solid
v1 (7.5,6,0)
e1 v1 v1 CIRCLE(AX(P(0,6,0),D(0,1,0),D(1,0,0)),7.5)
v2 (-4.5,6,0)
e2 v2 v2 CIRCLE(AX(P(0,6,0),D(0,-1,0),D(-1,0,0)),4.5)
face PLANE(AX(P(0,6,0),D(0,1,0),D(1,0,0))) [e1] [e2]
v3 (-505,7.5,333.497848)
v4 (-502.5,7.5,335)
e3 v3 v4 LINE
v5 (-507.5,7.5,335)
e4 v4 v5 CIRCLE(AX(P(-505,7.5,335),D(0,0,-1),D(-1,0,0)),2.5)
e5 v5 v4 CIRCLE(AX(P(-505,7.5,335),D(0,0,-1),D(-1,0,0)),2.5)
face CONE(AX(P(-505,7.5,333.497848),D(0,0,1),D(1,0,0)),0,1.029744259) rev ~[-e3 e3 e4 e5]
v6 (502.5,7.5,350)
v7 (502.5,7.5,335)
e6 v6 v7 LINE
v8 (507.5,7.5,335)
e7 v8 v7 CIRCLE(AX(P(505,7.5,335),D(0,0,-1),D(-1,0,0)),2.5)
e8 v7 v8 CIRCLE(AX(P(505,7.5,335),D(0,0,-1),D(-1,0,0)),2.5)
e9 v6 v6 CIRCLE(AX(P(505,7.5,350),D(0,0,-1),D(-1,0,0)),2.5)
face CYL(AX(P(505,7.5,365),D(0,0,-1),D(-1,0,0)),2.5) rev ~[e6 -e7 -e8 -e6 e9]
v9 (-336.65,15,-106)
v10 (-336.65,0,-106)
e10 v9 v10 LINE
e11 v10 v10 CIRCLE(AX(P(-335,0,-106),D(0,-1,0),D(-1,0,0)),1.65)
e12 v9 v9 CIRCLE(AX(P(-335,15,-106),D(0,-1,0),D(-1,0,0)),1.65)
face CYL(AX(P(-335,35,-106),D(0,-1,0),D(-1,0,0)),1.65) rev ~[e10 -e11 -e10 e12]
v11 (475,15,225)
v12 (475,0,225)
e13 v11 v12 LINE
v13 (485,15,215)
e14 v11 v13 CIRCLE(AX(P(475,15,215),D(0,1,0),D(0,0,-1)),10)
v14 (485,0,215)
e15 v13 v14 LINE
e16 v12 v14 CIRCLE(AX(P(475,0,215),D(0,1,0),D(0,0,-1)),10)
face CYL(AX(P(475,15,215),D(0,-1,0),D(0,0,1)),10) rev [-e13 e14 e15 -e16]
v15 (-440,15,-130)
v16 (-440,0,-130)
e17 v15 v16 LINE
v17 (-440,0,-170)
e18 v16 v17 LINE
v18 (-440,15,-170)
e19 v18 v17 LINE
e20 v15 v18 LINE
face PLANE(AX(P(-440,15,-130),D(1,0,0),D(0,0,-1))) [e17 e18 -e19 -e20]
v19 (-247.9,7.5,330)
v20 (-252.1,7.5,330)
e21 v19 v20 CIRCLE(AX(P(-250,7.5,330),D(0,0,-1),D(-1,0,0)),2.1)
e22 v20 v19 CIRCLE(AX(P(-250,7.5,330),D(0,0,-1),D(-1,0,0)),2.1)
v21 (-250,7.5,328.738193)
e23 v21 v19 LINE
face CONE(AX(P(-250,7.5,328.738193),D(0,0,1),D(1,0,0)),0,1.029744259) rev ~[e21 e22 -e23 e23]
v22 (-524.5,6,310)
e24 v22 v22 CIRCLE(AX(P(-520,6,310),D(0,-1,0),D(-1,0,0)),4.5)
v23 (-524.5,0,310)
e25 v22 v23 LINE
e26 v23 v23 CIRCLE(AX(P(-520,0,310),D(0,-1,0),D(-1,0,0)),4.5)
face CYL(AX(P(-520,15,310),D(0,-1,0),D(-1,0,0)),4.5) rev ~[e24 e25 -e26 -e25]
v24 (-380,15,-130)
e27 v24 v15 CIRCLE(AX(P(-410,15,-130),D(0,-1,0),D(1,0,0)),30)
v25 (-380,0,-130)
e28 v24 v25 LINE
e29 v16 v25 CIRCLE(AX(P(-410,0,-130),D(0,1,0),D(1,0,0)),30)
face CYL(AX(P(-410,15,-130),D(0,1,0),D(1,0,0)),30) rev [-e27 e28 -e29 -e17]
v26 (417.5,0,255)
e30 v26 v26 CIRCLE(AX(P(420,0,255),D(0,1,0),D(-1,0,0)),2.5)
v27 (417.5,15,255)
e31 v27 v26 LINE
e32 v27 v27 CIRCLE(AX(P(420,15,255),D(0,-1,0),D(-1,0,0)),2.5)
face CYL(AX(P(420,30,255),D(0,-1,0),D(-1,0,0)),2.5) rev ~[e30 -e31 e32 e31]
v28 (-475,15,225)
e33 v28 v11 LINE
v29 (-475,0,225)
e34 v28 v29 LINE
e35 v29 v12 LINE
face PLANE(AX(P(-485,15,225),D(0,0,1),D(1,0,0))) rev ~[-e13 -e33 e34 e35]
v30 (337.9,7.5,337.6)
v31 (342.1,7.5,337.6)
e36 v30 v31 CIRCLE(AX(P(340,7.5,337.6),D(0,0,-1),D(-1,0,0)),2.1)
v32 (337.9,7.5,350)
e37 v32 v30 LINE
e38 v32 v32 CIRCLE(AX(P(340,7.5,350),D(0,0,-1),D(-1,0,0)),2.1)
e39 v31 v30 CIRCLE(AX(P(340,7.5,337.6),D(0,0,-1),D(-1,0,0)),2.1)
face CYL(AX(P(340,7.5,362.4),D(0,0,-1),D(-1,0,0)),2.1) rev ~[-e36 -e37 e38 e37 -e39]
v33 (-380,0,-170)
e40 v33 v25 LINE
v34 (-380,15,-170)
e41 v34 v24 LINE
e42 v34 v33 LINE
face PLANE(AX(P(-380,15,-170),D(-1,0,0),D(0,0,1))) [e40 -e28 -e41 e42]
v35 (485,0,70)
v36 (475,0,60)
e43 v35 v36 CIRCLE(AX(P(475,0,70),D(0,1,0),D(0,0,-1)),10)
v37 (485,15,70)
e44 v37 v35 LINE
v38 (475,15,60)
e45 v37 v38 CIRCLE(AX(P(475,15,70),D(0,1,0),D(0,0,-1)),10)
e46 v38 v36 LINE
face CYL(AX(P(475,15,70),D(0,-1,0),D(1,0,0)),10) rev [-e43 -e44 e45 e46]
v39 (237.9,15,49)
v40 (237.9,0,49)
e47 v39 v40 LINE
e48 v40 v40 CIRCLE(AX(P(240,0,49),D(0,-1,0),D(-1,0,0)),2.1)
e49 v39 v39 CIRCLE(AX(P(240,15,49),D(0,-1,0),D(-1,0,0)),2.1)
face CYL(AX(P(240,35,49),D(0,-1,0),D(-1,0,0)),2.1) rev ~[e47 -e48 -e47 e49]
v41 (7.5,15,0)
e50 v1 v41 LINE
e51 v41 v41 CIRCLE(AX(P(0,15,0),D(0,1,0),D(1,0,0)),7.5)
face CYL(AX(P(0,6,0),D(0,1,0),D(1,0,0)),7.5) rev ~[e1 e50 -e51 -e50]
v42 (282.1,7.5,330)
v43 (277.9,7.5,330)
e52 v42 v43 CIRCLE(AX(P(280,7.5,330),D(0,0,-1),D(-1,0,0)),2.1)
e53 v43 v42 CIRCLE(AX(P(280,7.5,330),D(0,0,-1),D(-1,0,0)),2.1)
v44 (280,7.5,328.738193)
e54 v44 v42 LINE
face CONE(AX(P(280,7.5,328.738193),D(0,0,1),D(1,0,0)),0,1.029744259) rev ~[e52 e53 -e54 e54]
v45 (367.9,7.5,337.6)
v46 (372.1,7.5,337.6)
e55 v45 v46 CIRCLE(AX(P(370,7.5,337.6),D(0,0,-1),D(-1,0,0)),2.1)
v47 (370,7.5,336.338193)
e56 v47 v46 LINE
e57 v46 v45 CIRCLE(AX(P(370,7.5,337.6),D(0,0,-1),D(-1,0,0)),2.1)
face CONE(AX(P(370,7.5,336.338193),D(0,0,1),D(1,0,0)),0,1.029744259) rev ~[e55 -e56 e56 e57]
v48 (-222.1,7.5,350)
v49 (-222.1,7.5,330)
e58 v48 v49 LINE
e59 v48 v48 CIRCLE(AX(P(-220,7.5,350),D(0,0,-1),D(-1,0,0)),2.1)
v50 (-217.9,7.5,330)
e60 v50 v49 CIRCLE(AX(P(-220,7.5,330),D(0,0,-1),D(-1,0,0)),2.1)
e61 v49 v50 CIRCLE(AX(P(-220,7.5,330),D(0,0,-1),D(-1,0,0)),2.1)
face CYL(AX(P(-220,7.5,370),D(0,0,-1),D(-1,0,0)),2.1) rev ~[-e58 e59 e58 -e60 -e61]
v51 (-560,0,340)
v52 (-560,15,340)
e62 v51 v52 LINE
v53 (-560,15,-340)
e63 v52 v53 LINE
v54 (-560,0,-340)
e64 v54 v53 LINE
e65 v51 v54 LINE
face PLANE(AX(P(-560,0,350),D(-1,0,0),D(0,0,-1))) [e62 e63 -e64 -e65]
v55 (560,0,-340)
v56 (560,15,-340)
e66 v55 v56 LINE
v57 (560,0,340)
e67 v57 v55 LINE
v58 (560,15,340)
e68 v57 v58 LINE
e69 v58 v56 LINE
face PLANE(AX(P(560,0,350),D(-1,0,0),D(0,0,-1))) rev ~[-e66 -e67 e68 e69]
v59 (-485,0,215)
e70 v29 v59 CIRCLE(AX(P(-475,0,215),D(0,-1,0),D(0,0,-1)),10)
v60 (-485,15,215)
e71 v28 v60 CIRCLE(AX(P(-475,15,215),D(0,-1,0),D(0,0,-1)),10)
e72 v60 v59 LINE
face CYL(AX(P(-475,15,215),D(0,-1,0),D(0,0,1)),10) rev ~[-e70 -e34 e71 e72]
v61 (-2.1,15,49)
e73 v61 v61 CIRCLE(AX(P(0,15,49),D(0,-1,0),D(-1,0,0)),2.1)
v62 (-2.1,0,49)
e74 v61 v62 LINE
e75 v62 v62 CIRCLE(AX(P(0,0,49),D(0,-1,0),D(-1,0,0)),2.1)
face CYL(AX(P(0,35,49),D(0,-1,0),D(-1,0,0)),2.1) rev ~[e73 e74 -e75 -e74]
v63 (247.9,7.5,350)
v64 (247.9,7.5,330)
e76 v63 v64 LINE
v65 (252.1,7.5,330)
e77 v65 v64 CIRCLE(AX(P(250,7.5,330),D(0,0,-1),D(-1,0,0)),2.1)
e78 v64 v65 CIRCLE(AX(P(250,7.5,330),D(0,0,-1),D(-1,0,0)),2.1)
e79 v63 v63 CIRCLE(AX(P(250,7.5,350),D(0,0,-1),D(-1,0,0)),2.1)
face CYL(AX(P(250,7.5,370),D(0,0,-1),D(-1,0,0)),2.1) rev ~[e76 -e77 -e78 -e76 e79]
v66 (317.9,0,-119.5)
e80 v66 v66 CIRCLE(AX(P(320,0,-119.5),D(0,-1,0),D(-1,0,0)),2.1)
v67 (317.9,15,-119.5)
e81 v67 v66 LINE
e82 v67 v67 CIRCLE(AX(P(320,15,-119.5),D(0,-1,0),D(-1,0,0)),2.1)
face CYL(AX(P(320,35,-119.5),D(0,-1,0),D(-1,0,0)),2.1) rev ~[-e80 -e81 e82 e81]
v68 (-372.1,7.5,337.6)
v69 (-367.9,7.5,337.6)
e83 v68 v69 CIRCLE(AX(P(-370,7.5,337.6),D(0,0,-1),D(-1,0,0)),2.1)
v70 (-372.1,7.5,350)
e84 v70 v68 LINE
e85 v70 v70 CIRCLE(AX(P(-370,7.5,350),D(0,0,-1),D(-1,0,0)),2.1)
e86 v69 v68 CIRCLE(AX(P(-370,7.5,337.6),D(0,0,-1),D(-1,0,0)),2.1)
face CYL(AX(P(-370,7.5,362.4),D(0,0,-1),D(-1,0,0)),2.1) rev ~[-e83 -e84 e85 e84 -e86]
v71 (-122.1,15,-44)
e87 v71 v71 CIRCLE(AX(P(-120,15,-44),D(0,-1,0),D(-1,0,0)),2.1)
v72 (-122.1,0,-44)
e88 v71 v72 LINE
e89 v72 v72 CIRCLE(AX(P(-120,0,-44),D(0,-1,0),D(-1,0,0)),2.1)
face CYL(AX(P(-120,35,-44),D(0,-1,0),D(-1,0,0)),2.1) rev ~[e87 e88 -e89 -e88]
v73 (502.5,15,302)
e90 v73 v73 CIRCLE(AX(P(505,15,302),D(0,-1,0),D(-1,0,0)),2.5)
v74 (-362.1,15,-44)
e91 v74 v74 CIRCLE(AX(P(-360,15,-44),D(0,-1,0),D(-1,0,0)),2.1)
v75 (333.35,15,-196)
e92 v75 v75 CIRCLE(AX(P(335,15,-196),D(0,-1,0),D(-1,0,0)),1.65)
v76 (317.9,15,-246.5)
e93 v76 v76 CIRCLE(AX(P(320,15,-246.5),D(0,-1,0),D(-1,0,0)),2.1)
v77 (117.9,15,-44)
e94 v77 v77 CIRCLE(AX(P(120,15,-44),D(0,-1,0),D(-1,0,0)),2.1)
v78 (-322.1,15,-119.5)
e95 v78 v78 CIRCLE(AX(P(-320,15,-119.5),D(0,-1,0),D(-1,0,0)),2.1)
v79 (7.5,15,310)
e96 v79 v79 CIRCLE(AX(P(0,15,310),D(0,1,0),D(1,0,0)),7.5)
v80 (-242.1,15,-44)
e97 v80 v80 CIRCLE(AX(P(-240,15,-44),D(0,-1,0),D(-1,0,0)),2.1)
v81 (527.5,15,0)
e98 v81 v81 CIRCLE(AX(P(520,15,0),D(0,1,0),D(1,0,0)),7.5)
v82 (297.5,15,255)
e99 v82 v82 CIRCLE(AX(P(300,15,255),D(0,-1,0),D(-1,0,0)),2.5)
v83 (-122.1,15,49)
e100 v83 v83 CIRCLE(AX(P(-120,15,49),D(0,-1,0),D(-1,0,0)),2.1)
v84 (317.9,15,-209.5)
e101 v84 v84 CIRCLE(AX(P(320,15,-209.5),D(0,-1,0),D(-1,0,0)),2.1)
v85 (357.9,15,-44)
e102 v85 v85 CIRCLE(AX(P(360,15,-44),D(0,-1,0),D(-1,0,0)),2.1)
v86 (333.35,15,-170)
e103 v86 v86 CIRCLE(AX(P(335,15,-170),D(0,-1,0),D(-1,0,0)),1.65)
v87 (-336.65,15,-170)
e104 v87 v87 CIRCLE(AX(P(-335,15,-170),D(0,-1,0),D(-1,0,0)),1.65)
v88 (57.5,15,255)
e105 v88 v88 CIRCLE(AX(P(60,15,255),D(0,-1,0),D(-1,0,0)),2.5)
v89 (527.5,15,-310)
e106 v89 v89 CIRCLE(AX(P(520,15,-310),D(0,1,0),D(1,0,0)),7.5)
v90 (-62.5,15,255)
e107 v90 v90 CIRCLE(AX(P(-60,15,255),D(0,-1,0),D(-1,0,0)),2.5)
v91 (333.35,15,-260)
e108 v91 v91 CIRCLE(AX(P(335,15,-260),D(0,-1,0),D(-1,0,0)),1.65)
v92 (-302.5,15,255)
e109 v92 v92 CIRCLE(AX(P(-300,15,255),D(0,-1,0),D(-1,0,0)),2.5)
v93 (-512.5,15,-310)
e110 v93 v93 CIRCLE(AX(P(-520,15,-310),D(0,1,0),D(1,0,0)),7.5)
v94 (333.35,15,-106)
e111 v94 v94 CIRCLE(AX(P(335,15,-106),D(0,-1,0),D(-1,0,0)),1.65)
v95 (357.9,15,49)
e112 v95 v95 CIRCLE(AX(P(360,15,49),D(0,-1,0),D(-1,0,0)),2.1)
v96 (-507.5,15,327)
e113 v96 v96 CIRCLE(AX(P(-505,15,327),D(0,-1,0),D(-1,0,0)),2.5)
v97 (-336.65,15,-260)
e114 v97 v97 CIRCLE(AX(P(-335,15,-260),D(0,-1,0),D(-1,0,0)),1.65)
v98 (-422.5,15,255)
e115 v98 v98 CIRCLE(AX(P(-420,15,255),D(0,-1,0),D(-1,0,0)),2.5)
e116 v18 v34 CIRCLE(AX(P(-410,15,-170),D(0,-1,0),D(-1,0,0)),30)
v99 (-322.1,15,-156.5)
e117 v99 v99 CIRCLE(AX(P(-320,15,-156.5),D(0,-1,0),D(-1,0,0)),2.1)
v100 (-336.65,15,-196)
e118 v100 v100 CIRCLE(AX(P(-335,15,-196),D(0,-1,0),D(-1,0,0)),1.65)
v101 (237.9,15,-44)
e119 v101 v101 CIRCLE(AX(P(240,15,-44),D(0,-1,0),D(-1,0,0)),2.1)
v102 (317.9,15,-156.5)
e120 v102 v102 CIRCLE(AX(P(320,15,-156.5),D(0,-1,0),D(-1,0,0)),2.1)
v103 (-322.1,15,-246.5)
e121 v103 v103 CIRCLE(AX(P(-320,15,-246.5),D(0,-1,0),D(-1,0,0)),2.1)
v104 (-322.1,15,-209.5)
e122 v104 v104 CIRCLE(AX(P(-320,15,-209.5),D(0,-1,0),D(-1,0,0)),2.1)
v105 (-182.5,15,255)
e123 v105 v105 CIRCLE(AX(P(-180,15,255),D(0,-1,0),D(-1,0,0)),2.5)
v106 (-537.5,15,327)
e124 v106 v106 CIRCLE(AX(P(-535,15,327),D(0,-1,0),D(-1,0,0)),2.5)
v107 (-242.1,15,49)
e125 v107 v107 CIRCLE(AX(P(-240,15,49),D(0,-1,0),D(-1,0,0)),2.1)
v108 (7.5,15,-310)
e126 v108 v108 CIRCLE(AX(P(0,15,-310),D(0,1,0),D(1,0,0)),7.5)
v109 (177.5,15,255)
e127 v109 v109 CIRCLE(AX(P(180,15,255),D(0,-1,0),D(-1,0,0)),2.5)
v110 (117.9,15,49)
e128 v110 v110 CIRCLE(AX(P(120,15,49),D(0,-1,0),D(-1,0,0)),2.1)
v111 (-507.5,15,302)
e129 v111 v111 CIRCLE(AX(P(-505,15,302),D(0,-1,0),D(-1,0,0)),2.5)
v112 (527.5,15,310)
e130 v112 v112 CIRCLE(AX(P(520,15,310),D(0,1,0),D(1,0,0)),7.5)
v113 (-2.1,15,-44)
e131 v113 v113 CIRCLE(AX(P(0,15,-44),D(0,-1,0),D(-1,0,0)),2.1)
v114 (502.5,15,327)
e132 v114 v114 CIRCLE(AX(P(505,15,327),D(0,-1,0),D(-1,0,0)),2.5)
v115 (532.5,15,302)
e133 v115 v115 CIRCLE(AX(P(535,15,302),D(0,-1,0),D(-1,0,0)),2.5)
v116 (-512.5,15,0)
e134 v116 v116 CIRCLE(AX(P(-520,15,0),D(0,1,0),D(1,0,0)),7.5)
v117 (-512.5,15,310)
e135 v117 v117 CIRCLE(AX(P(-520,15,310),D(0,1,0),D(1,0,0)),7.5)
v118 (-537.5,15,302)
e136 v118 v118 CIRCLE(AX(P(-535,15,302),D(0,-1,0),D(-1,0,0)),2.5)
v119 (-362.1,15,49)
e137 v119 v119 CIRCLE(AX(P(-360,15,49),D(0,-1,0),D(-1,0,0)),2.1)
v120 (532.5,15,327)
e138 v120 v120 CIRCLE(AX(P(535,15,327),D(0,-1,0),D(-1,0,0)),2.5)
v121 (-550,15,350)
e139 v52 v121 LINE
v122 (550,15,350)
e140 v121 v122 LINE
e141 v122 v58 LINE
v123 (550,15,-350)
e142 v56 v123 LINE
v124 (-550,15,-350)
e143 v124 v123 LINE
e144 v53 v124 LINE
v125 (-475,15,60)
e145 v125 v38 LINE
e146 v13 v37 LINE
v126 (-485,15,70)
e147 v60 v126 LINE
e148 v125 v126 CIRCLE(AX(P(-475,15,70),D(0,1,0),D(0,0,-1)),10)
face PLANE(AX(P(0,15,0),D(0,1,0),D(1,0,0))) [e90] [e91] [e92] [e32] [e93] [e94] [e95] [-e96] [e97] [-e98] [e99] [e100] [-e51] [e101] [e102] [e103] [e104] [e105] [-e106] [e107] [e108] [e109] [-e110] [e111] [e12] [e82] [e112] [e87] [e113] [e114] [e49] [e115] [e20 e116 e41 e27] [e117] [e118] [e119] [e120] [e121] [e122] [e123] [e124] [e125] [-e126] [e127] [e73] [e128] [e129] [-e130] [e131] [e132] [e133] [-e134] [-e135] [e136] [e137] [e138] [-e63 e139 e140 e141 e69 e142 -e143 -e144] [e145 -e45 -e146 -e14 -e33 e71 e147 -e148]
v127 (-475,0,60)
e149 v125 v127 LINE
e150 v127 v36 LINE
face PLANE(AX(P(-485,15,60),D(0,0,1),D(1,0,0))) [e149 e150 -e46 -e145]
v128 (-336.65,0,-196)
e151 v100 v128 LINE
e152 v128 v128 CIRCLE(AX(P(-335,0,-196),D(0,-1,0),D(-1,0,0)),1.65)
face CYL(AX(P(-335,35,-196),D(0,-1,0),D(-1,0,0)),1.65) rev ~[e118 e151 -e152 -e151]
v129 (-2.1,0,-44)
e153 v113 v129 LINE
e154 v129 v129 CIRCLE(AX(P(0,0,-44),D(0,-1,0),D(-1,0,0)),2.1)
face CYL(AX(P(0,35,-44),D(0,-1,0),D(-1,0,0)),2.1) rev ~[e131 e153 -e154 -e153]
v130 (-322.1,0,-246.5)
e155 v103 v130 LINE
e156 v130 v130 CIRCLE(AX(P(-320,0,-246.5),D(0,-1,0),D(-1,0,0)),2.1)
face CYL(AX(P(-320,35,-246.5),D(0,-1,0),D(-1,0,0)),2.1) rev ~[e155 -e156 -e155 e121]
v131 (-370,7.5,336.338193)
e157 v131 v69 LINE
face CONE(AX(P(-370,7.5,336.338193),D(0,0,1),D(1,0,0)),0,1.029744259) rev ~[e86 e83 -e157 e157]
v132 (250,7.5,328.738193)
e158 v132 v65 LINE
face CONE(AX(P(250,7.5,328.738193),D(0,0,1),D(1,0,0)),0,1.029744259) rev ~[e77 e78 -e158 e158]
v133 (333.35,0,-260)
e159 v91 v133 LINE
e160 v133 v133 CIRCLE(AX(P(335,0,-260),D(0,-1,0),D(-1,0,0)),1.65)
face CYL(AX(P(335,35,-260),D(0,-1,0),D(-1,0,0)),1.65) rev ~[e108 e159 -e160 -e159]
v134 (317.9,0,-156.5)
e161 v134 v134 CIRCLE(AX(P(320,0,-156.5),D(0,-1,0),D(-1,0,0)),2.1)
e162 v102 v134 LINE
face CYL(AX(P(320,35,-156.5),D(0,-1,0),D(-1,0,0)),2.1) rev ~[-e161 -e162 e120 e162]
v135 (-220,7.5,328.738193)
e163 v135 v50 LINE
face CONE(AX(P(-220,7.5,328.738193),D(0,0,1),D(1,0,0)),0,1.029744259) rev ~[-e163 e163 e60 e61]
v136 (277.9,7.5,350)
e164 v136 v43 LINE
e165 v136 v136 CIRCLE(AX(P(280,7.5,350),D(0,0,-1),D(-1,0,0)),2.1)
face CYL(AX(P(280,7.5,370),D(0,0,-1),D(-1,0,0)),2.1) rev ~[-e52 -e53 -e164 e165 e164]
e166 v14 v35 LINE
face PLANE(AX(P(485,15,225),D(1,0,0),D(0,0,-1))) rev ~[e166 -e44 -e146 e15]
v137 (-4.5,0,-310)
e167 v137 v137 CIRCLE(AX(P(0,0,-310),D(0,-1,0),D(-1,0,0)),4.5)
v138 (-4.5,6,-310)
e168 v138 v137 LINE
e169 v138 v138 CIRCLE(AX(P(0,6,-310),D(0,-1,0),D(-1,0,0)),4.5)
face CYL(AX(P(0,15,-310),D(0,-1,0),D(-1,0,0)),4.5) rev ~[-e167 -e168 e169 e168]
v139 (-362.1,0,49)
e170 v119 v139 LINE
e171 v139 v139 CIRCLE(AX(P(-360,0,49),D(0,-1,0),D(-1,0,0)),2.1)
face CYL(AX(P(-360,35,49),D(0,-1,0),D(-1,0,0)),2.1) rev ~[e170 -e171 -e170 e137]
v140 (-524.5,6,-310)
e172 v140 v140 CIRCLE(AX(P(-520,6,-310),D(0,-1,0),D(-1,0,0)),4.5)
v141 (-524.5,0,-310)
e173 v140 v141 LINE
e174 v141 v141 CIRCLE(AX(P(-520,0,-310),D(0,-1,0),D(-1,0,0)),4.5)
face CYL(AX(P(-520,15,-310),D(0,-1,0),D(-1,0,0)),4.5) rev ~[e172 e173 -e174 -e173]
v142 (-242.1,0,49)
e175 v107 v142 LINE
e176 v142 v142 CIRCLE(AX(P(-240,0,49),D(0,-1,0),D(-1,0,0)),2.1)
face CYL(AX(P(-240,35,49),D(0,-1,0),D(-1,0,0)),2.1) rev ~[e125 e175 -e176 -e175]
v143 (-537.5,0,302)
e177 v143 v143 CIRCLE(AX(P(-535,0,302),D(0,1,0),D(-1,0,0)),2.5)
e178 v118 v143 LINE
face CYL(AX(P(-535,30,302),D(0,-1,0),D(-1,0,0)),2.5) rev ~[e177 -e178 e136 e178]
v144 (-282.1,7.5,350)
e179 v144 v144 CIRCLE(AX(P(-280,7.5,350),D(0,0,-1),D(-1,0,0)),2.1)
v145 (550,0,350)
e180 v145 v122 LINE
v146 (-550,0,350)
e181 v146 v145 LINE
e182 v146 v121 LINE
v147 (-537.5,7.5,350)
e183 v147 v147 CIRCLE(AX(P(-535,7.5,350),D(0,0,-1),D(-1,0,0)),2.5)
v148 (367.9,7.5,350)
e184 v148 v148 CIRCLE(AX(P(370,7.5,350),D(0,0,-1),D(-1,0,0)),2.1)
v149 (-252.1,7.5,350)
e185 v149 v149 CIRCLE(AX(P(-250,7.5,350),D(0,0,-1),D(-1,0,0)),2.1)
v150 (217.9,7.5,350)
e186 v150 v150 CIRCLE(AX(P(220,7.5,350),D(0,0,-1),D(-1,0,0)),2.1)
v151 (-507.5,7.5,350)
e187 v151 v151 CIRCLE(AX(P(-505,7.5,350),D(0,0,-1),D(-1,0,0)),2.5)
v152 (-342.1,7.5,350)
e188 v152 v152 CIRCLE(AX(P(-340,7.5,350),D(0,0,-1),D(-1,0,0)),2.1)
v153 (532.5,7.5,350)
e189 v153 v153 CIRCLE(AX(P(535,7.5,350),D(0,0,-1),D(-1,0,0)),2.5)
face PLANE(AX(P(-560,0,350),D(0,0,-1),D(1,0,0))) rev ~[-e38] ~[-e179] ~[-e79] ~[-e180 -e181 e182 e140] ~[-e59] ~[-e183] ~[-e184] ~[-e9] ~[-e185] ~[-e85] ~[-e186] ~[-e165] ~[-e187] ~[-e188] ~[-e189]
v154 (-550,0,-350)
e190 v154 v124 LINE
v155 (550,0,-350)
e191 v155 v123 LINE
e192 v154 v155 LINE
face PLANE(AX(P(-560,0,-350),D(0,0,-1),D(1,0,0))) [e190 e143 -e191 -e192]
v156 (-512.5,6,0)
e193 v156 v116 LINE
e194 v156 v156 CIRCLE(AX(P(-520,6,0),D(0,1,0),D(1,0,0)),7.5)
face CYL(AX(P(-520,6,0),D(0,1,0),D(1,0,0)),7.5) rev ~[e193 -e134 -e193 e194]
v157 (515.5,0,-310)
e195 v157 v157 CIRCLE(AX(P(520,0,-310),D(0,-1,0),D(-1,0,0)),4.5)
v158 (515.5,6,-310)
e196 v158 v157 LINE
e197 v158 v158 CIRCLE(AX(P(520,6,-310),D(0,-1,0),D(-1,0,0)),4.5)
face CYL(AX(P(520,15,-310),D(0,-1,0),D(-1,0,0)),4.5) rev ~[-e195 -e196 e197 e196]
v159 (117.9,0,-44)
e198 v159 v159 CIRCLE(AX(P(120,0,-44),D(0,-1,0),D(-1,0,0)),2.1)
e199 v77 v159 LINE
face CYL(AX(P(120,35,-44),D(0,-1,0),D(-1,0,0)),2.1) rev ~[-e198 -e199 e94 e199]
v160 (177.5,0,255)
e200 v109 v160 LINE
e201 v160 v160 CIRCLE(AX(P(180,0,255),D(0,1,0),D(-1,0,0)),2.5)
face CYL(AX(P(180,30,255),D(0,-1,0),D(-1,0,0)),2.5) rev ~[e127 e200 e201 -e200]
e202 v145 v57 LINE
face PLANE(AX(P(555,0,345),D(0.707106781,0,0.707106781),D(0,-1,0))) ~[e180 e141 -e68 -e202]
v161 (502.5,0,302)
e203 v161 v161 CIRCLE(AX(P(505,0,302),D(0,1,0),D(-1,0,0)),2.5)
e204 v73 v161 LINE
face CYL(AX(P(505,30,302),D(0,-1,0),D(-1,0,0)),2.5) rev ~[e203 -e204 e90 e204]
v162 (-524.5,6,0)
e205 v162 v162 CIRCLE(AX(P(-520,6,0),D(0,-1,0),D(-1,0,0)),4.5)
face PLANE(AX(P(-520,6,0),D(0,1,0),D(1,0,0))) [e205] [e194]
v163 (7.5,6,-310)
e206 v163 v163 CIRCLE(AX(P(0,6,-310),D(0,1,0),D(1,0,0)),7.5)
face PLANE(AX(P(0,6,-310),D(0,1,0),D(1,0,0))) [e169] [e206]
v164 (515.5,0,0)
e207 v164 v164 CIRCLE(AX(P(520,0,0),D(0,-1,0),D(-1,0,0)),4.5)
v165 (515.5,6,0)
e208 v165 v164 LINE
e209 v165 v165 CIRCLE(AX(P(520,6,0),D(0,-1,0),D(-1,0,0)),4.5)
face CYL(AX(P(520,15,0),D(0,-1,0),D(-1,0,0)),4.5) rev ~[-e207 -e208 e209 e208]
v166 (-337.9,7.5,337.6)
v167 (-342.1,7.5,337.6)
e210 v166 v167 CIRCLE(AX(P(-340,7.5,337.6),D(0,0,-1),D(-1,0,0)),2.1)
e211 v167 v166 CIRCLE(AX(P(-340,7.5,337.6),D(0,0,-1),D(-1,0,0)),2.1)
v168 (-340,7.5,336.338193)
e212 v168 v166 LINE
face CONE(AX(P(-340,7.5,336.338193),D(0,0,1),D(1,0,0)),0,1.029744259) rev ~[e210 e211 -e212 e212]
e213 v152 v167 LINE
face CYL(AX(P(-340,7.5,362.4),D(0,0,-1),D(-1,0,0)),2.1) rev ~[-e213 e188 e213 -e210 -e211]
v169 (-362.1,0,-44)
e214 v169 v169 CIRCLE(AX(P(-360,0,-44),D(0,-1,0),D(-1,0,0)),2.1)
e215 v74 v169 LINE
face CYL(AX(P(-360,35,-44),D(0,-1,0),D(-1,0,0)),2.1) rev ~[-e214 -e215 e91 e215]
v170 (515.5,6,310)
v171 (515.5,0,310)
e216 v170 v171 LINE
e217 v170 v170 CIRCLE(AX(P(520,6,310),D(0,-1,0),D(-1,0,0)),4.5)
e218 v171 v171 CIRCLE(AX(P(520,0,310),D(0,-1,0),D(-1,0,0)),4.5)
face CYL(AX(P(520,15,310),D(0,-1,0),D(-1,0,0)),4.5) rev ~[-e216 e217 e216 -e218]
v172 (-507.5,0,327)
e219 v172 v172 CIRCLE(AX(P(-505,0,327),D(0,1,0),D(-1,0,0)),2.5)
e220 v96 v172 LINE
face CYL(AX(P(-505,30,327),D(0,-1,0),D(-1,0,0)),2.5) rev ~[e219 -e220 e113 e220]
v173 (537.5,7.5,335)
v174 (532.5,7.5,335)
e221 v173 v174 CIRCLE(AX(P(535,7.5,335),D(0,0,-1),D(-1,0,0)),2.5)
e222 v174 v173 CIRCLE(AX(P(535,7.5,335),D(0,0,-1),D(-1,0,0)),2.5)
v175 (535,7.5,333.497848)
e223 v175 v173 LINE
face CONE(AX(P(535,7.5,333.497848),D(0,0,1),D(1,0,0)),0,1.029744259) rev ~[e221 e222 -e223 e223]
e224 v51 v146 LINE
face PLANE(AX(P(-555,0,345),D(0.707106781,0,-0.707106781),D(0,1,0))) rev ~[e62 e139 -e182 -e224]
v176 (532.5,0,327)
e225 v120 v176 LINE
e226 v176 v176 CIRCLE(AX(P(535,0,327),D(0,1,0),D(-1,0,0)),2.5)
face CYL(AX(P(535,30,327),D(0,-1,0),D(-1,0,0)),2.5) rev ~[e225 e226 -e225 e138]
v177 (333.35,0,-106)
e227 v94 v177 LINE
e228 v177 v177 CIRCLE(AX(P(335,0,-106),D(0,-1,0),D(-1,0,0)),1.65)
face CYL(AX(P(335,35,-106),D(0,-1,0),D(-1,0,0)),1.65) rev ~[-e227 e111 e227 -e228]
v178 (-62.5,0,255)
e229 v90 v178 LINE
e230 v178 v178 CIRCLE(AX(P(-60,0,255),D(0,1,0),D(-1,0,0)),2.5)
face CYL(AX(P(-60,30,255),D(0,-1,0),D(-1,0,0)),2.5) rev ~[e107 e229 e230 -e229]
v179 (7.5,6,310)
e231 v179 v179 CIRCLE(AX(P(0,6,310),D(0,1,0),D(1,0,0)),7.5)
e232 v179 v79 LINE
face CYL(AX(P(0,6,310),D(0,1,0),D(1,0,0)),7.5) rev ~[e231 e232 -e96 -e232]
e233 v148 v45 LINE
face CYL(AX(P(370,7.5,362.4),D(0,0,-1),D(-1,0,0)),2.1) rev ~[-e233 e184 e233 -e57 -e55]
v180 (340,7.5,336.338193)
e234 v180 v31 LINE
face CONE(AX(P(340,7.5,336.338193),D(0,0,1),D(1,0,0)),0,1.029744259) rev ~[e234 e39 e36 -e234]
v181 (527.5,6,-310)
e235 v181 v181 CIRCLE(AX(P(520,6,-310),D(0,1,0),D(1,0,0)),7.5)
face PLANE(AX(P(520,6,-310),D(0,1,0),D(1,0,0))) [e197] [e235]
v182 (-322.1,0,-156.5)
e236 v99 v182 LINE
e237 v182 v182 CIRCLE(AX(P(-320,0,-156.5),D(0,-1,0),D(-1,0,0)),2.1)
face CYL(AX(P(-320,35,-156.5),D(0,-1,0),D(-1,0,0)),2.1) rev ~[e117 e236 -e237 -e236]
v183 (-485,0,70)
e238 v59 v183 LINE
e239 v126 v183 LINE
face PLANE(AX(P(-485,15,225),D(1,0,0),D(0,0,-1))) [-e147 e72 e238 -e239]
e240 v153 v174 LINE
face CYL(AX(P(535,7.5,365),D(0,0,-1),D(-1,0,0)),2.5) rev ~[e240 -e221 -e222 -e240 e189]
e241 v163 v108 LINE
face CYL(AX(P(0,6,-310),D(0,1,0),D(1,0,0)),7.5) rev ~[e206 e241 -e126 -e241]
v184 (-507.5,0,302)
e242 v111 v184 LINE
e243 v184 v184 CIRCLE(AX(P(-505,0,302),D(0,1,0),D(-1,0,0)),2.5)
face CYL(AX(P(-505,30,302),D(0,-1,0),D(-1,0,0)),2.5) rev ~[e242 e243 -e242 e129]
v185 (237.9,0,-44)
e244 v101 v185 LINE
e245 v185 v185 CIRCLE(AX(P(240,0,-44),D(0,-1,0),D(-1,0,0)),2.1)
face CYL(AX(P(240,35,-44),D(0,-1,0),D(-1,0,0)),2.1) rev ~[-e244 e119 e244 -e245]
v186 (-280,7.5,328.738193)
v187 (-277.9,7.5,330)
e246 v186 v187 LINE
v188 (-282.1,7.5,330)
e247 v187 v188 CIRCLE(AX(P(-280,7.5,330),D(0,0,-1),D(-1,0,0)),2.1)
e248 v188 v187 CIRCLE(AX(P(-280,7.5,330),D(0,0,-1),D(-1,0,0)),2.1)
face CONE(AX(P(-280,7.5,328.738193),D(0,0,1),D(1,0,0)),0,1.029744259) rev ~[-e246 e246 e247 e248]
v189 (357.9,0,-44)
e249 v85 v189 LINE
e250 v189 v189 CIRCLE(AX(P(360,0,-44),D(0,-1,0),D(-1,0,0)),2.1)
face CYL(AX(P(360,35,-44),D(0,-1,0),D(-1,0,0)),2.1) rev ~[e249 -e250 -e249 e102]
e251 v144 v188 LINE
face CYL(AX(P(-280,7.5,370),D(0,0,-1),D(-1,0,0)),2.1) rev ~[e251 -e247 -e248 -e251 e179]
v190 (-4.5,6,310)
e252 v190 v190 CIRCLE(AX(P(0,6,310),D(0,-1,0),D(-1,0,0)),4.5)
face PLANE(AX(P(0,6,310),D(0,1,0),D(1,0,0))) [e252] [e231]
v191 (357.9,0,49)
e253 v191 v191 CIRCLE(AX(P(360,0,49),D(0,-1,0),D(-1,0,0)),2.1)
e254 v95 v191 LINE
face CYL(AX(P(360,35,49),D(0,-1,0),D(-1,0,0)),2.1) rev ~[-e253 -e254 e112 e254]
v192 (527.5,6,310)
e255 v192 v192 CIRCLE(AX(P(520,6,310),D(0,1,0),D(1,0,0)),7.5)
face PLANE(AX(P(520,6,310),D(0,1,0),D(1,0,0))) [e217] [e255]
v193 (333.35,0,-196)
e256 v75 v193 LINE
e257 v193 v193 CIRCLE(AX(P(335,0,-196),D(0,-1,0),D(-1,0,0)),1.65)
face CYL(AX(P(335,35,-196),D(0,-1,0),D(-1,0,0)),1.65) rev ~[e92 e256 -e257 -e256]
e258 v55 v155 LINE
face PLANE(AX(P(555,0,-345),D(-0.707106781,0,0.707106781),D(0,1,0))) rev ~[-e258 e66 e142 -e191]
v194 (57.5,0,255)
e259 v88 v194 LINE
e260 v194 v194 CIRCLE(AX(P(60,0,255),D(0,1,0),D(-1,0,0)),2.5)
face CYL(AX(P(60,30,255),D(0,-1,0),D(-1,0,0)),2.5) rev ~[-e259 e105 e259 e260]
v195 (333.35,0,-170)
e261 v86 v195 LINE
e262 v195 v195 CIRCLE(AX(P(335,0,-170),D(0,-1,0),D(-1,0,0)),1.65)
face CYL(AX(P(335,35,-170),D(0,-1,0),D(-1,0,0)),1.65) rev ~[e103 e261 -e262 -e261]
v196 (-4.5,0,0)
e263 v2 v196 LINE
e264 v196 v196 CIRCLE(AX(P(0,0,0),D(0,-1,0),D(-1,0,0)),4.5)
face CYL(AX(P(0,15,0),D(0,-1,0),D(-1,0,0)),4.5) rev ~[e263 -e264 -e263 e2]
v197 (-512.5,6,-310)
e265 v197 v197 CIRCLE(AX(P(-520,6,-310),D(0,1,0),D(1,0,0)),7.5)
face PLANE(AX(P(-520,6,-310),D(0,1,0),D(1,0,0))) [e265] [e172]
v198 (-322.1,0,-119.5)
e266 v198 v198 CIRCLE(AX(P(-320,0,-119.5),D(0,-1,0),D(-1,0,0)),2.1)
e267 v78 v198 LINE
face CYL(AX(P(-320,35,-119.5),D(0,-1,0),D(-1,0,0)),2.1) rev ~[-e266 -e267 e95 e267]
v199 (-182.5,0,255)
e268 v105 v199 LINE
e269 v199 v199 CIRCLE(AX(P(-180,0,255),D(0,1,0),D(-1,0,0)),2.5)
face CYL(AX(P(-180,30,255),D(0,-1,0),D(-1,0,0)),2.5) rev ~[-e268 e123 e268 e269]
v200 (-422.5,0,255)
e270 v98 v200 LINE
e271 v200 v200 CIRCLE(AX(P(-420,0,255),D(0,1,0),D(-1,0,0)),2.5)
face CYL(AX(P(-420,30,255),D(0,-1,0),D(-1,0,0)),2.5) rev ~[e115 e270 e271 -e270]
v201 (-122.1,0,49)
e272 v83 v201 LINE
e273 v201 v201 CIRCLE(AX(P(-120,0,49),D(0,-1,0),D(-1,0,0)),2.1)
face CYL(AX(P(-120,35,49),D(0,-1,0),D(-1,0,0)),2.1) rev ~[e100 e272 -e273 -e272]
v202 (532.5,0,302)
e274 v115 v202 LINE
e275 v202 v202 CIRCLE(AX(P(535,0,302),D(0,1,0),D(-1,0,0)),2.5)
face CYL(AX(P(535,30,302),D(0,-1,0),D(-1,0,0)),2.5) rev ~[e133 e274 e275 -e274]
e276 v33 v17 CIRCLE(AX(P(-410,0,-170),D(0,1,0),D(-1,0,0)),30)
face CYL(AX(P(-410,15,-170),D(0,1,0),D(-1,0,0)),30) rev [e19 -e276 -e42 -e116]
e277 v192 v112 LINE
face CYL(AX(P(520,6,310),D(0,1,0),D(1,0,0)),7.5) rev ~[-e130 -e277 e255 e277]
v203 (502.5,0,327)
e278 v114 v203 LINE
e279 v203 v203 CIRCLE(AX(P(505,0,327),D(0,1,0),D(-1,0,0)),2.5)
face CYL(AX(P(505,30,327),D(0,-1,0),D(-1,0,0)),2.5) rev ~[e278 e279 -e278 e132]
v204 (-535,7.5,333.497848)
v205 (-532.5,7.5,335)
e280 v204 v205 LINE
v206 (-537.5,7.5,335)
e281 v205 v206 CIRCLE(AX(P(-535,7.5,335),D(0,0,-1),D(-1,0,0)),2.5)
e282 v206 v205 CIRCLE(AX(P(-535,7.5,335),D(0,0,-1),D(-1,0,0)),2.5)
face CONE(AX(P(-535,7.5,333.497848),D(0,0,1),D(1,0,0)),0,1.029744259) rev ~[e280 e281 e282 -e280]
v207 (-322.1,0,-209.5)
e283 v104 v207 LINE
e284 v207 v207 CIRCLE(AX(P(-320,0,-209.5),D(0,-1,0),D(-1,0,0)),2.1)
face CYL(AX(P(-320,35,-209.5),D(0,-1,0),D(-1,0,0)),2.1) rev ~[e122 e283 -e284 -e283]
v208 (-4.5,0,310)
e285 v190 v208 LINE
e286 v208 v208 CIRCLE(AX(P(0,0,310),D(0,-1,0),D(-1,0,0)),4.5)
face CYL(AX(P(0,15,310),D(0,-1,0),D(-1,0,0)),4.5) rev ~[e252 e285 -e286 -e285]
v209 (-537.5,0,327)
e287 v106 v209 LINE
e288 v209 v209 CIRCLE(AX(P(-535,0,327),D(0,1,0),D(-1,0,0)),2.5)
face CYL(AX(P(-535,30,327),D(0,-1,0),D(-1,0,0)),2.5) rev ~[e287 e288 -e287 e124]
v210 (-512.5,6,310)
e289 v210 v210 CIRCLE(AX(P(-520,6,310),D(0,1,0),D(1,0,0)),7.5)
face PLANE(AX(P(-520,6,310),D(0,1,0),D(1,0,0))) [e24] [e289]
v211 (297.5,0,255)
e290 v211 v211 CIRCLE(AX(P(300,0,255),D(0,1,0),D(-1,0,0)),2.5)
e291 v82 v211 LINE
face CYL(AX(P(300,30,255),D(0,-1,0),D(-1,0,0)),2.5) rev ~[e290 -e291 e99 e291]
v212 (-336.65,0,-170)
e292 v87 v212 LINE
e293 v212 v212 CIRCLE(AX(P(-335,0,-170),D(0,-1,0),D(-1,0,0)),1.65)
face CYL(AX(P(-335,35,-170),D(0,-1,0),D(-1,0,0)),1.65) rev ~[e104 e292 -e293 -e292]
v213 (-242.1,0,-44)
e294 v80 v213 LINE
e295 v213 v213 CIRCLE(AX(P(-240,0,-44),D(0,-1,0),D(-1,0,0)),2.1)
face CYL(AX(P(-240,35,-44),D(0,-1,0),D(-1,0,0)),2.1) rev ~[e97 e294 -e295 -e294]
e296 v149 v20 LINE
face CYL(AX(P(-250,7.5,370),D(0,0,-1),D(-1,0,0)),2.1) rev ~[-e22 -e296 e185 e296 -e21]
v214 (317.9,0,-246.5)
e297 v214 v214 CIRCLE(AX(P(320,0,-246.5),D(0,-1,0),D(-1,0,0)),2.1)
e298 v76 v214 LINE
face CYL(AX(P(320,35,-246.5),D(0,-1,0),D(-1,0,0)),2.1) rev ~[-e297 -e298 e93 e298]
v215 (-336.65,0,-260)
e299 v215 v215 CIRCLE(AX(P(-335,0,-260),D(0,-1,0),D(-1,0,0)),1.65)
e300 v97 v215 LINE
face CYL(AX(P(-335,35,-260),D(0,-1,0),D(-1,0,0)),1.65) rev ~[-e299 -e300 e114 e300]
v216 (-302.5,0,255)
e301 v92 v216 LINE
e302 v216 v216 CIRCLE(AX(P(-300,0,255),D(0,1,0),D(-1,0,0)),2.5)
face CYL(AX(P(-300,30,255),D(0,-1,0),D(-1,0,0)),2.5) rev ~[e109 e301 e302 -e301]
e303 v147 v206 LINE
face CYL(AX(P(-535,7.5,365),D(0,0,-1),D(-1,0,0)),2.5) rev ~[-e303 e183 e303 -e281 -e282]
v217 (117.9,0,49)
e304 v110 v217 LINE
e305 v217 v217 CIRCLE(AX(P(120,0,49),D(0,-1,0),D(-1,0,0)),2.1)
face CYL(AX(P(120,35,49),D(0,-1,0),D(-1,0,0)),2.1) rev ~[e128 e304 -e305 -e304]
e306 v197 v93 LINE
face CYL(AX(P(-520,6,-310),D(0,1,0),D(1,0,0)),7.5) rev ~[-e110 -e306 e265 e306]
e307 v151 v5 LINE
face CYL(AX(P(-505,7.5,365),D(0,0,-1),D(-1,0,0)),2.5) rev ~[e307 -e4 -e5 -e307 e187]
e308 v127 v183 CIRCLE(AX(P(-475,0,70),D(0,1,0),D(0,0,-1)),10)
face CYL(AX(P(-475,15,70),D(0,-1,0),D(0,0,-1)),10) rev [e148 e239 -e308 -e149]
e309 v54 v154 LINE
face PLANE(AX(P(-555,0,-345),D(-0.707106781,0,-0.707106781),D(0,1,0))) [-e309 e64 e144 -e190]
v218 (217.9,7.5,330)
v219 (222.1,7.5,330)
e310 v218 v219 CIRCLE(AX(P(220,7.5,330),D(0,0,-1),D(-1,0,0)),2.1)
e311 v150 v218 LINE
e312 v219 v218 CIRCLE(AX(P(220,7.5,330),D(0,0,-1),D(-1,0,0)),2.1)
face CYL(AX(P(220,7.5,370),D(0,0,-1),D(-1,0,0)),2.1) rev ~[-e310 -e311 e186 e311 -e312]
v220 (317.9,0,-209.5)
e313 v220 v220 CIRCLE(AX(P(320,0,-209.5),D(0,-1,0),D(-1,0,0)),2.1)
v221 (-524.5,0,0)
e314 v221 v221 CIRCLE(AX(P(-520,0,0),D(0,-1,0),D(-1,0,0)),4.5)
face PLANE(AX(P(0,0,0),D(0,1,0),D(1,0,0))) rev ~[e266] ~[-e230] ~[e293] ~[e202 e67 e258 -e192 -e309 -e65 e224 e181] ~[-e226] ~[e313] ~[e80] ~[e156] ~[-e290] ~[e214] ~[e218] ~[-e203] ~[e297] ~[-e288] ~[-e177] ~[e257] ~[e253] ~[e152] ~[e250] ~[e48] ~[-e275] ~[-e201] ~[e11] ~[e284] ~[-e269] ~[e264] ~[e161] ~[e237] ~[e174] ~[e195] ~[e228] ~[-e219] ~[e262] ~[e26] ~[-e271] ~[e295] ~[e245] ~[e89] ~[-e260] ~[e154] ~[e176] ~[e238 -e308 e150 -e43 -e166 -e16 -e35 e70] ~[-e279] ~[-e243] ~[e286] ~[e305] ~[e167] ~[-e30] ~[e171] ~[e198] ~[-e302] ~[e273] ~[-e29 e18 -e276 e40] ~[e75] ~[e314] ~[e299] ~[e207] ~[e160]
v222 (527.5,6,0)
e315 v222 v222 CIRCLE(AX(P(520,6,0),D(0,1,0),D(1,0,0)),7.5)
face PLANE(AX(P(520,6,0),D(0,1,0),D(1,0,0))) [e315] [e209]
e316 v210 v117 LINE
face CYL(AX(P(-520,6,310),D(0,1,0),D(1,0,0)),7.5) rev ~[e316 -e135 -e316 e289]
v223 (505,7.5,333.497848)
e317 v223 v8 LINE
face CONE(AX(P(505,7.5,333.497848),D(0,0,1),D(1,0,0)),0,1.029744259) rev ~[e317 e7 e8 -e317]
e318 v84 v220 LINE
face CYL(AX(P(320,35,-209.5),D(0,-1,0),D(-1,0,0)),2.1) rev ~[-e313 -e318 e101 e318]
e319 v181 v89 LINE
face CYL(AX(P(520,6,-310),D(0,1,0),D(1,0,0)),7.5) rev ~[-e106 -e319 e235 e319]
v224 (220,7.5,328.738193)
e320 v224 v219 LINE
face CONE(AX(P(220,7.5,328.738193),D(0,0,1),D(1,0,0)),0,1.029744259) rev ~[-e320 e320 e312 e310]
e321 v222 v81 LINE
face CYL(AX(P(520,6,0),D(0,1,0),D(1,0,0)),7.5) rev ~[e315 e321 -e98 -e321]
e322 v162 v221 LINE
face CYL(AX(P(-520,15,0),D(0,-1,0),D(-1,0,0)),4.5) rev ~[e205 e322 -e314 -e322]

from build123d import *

# Parameters (mm, degrees)
SKETCH_1_W                = 1120
SKETCH_1_H                = 700
EXTRUDE_1_DEPTH           = 15
CHAMFER_1_SIZE            = 10
SKETCH_2_W                = 970
SKETCH_2_H                = 165
CUT_EXTRUDE_1_DEPTH       = 20
FILLET_1_R                = 10
HOLE_WIZARD_1_D           = 9
HOLE_WIZARD_1_DEPTH       = 19.75
HOLE_WIZARD_1_CBORE_D     = 15
HOLE_WIZARD_1_CBORE_DEPTH = 9
HOLE_WIZARD_1_TIP         = 2.703872786
HOLE_WIZARD_M6_1_D        = 5
HOLE_WIZARD_M6_1_DEPTH    = 15
HOLE_WIZARD_M6_1_TIP      = 1.502151548
HOLE_WIZARD_M5_1_D        = 4.2
HOLE_WIZARD_M5_1_DEPTH    = 20
HOLE_WIZARD_M5_1_TIP      = 1.2618073
CUT_EXTRUDE_2_DEPTH       = 20
HOLE_WIZARD_M5_2_D        = 4.2
HOLE_WIZARD_M5_2_DEPTH    = 20
HOLE_WIZARD_M5_2_TIP      = 1.2618073
HOLE_WIZARD_M4_1_D        = 3.3
HOLE_WIZARD_M4_1_DEPTH    = 20
HOLE_WIZARD_M4_1_TIP      = 0.991420021
HOLE_WIZARD_M5_3_D        = 4.2
HOLE_WIZARD_M5_3_DEPTH    = 20
HOLE_WIZARD_M5_3_TIP      = 1.2618073
HOLE_WIZARD_M5_4_D        = 4.2
HOLE_WIZARD_M5_4_DEPTH    = 12.4
HOLE_WIZARD_M5_4_TIP      = 1.2618073
HOLE_WIZARD_2_D           = 9
HOLE_WIZARD_2_DEPTH       = 19.75
HOLE_WIZARD_2_CBORE_D     = 15
HOLE_WIZARD_2_CBORE_DEPTH = 9
HOLE_WIZARD_2_TIP         = 2.703872786
HOLE_WIZARD_M6_2_D        = 5
HOLE_WIZARD_M6_2_DEPTH    = 15
HOLE_WIZARD_M6_2_TIP      = 1.502151548
HOLE_WIZARD_M6_3_D        = 5
HOLE_WIZARD_M6_3_DEPTH    = 15
HOLE_WIZARD_M6_3_TIP      = 1.502151548


with BuildPart() as part:
    # 草图1 → 凸台-拉伸1 (new body)
    with BuildSketch(Plane(origin=(0, 0, 0), x_dir=(1, 0, 0), z_dir=(0, 1, 0))):
        Rectangle(SKETCH_1_W, SKETCH_1_H)
    extrude(amount=EXTRUDE_1_DEPTH)

    # 倒角1
    chamfer_1_edges = [part.edges().sort_by_distance(p)[0] for p in [
        (560, 7.5, 350),
        (-560, 7.5, 350),
        (-560, 7.5, -350),
        (560, 7.5, -350),
    ]]
    chamfer(chamfer_1_edges, length=CHAMFER_1_SIZE)

    # 草图2 → 切除-拉伸1 (cut)
    with BuildSketch(Plane(origin=(0, 15, 0), x_dir=(1, 0, 0), z_dir=(0, 1, 0))):
        with Locations((0, -142.5)):
            Rectangle(SKETCH_2_W, SKETCH_2_H)
    extrude(amount=-CUT_EXTRUDE_1_DEPTH, mode=Mode.SUBTRACT)

    # 圆角1
    fillet_1_edges = [part.edges().sort_by_distance(p)[0] for p in [
        (485, 7.5, 60),
        (485, 7.5, 225),
        (-485, 7.5, 225),
        (-485, 7.5, 60),
    ]]
    fillet(fillet_1_edges, radius=FILLET_1_R)

    # 打孔尺寸(%根据)内六角圆柱头螺钉的类型1
    with Locations(Plane(origin=(0, 15, 0), x_dir=(1, 0, 0), z_dir=(0, 1, 0))):
        with Locations((520, -310), (520, 0), (520, 310), (-520, -310), (-520, 0), (-520, 310)):
            CounterBoreHole(HOLE_WIZARD_1_D / 2, HOLE_WIZARD_1_CBORE_D / 2, HOLE_WIZARD_1_CBORE_DEPTH, depth=HOLE_WIZARD_1_DEPTH)
            with Locations((0, 0, -(HOLE_WIZARD_1_DEPTH + HOLE_WIZARD_1_TIP / 2))):  # 118° drill point
                Cone(0, HOLE_WIZARD_1_D / 2, HOLE_WIZARD_1_TIP, mode=Mode.SUBTRACT)

    # M6 螺纹孔1
    with Locations(Plane(origin=(0, 15, 0), x_dir=(1, 0, 0), z_dir=(0, 1, 0))):
        with Locations((-420, -255), (-300, -255), (-180, -255), (-60, -255), (60, -255), (180, -255), (300, -255), (420, -255)):
            Hole(HOLE_WIZARD_M6_1_D / 2, depth=HOLE_WIZARD_M6_1_DEPTH)
            with Locations((0, 0, -(HOLE_WIZARD_M6_1_DEPTH + HOLE_WIZARD_M6_1_TIP / 2))):  # 118° drill point
                Cone(0, HOLE_WIZARD_M6_1_D / 2, HOLE_WIZARD_M6_1_TIP, mode=Mode.SUBTRACT)

    # M5 螺纹孔1
    with Locations(Plane(origin=(0, 15, 0), x_dir=(1, 0, 0), z_dir=(0, 1, 0))):
        with Locations((360, -49), (360, 44), (240, -49), (240, 44), (120, -49), (120, 44), (0, -49), (0, 44), (-120, -49), (-120, 44), (-240, -49), (-240, 44), (-360, -49), (-360, 44)):
            Hole(HOLE_WIZARD_M5_1_D / 2, depth=HOLE_WIZARD_M5_1_DEPTH)
            with Locations((0, 0, -(HOLE_WIZARD_M5_1_DEPTH + HOLE_WIZARD_M5_1_TIP / 2))):  # 118° drill point
                Cone(0, HOLE_WIZARD_M5_1_D / 2, HOLE_WIZARD_M5_1_TIP, mode=Mode.SUBTRACT)

    # 草图9 → 切除-拉伸2 (cut)
    with BuildSketch(Plane(origin=(0, 15, 0), x_dir=(1, 0, 0), z_dir=(0, 1, 0))):
        with BuildLine():
            Line((-440, 130), (-440, 170))
            ThreePointArc((-440, 170), (-410, 200), (-380, 170))
            Line((-380, 170), (-380, 130))
            ThreePointArc((-380, 130), (-410, 100), (-440, 130))
        make_face()
    extrude(amount=-CUT_EXTRUDE_2_DEPTH, mode=Mode.SUBTRACT)

    # M5 螺纹孔2
    with Locations(Plane.XY.offset(350)):
        with Locations((-280, 7.5), (-250, 7.5), (-220, 7.5), (280, 7.5), (250, 7.5), (220, 7.5)):
            Hole(HOLE_WIZARD_M5_2_D / 2, depth=HOLE_WIZARD_M5_2_DEPTH)
            with Locations((0, 0, -(HOLE_WIZARD_M5_2_DEPTH + HOLE_WIZARD_M5_2_TIP / 2))):  # 118° drill point
                Cone(0, HOLE_WIZARD_M5_2_D / 2, HOLE_WIZARD_M5_2_TIP, mode=Mode.SUBTRACT)

    # M4 螺纹孔1
    with Locations(Plane(origin=(0, 15, 0), x_dir=(1, 0, 0), z_dir=(0, 1, 0))):
        with Locations((335, 106), (335, 170), (-335, 106), (-335, 170), (-335, 196), (-335, 260), (335, 196), (335, 260)):
            Hole(HOLE_WIZARD_M4_1_D / 2, depth=HOLE_WIZARD_M4_1_DEPTH)
            with Locations((0, 0, -(HOLE_WIZARD_M4_1_DEPTH + HOLE_WIZARD_M4_1_TIP / 2))):  # 118° drill point
                Cone(0, HOLE_WIZARD_M4_1_D / 2, HOLE_WIZARD_M4_1_TIP, mode=Mode.SUBTRACT)

    # M5 螺纹孔3
    with Locations(Plane(origin=(0, 15, 0), x_dir=(1, 0, 0), z_dir=(0, 1, 0))):
        with Locations((320, 119.5), (320, 156.5), (320, 209.5), (320, 246.5), (-320, 119.5), (-320, 156.5), (-320, 209.5), (-320, 246.5)):
            Hole(HOLE_WIZARD_M5_3_D / 2, depth=HOLE_WIZARD_M5_3_DEPTH)
            with Locations((0, 0, -(HOLE_WIZARD_M5_3_DEPTH + HOLE_WIZARD_M5_3_TIP / 2))):  # 118° drill point
                Cone(0, HOLE_WIZARD_M5_3_D / 2, HOLE_WIZARD_M5_3_TIP, mode=Mode.SUBTRACT)

    # M5 螺纹孔4
    with Locations(Plane.XY.offset(350)):
        with Locations((-370, 7.5), (-340, 7.5), (370, 7.5), (340, 7.5)):
            Hole(HOLE_WIZARD_M5_4_D / 2, depth=HOLE_WIZARD_M5_4_DEPTH)
            with Locations((0, 0, -(HOLE_WIZARD_M5_4_DEPTH + HOLE_WIZARD_M5_4_TIP / 2))):  # 118° drill point
                Cone(0, HOLE_WIZARD_M5_4_D / 2, HOLE_WIZARD_M5_4_TIP, mode=Mode.SUBTRACT)

    # 打孔尺寸(%根据)内六角圆柱头螺钉的类型2
    with Locations(Plane(origin=(0, 15, 0), x_dir=(1, 0, 0), z_dir=(0, 1, 0))):
        with Locations((0, 310), (0, 0), (0, -310)):
            CounterBoreHole(HOLE_WIZARD_2_D / 2, HOLE_WIZARD_2_CBORE_D / 2, HOLE_WIZARD_2_CBORE_DEPTH, depth=HOLE_WIZARD_2_DEPTH)
            with Locations((0, 0, -(HOLE_WIZARD_2_DEPTH + HOLE_WIZARD_2_TIP / 2))):  # 118° drill point
                Cone(0, HOLE_WIZARD_2_D / 2, HOLE_WIZARD_2_TIP, mode=Mode.SUBTRACT)

    # M6 螺纹孔2
    with Locations(Plane.XY.offset(350)):
        with Locations((-535, 7.5), (-505, 7.5), (505, 7.5), (535, 7.5)):
            Hole(HOLE_WIZARD_M6_2_D / 2, depth=HOLE_WIZARD_M6_2_DEPTH)
            with Locations((0, 0, -(HOLE_WIZARD_M6_2_DEPTH + HOLE_WIZARD_M6_2_TIP / 2))):  # 118° drill point
                Cone(0, HOLE_WIZARD_M6_2_D / 2, HOLE_WIZARD_M6_2_TIP, mode=Mode.SUBTRACT)

    # M6 螺纹孔3
    with Locations(Plane(origin=(0, 15, 0), x_dir=(1, 0, 0), z_dir=(0, 1, 0))):
        with Locations((535, -327), (505, -327), (535, -302), (505, -302), (-505, -327), (-535, -327), (-505, -302), (-535, -302)):
            Hole(HOLE_WIZARD_M6_3_D / 2, depth=HOLE_WIZARD_M6_3_DEPTH)
            with Locations((0, 0, -(HOLE_WIZARD_M6_3_DEPTH + HOLE_WIZARD_M6_3_TIP / 2))):  # 118° drill point
                Cone(0, HOLE_WIZARD_M6_3_D / 2, HOLE_WIZARD_M6_3_TIP, mode=Mode.SUBTRACT)


solid = part.part
